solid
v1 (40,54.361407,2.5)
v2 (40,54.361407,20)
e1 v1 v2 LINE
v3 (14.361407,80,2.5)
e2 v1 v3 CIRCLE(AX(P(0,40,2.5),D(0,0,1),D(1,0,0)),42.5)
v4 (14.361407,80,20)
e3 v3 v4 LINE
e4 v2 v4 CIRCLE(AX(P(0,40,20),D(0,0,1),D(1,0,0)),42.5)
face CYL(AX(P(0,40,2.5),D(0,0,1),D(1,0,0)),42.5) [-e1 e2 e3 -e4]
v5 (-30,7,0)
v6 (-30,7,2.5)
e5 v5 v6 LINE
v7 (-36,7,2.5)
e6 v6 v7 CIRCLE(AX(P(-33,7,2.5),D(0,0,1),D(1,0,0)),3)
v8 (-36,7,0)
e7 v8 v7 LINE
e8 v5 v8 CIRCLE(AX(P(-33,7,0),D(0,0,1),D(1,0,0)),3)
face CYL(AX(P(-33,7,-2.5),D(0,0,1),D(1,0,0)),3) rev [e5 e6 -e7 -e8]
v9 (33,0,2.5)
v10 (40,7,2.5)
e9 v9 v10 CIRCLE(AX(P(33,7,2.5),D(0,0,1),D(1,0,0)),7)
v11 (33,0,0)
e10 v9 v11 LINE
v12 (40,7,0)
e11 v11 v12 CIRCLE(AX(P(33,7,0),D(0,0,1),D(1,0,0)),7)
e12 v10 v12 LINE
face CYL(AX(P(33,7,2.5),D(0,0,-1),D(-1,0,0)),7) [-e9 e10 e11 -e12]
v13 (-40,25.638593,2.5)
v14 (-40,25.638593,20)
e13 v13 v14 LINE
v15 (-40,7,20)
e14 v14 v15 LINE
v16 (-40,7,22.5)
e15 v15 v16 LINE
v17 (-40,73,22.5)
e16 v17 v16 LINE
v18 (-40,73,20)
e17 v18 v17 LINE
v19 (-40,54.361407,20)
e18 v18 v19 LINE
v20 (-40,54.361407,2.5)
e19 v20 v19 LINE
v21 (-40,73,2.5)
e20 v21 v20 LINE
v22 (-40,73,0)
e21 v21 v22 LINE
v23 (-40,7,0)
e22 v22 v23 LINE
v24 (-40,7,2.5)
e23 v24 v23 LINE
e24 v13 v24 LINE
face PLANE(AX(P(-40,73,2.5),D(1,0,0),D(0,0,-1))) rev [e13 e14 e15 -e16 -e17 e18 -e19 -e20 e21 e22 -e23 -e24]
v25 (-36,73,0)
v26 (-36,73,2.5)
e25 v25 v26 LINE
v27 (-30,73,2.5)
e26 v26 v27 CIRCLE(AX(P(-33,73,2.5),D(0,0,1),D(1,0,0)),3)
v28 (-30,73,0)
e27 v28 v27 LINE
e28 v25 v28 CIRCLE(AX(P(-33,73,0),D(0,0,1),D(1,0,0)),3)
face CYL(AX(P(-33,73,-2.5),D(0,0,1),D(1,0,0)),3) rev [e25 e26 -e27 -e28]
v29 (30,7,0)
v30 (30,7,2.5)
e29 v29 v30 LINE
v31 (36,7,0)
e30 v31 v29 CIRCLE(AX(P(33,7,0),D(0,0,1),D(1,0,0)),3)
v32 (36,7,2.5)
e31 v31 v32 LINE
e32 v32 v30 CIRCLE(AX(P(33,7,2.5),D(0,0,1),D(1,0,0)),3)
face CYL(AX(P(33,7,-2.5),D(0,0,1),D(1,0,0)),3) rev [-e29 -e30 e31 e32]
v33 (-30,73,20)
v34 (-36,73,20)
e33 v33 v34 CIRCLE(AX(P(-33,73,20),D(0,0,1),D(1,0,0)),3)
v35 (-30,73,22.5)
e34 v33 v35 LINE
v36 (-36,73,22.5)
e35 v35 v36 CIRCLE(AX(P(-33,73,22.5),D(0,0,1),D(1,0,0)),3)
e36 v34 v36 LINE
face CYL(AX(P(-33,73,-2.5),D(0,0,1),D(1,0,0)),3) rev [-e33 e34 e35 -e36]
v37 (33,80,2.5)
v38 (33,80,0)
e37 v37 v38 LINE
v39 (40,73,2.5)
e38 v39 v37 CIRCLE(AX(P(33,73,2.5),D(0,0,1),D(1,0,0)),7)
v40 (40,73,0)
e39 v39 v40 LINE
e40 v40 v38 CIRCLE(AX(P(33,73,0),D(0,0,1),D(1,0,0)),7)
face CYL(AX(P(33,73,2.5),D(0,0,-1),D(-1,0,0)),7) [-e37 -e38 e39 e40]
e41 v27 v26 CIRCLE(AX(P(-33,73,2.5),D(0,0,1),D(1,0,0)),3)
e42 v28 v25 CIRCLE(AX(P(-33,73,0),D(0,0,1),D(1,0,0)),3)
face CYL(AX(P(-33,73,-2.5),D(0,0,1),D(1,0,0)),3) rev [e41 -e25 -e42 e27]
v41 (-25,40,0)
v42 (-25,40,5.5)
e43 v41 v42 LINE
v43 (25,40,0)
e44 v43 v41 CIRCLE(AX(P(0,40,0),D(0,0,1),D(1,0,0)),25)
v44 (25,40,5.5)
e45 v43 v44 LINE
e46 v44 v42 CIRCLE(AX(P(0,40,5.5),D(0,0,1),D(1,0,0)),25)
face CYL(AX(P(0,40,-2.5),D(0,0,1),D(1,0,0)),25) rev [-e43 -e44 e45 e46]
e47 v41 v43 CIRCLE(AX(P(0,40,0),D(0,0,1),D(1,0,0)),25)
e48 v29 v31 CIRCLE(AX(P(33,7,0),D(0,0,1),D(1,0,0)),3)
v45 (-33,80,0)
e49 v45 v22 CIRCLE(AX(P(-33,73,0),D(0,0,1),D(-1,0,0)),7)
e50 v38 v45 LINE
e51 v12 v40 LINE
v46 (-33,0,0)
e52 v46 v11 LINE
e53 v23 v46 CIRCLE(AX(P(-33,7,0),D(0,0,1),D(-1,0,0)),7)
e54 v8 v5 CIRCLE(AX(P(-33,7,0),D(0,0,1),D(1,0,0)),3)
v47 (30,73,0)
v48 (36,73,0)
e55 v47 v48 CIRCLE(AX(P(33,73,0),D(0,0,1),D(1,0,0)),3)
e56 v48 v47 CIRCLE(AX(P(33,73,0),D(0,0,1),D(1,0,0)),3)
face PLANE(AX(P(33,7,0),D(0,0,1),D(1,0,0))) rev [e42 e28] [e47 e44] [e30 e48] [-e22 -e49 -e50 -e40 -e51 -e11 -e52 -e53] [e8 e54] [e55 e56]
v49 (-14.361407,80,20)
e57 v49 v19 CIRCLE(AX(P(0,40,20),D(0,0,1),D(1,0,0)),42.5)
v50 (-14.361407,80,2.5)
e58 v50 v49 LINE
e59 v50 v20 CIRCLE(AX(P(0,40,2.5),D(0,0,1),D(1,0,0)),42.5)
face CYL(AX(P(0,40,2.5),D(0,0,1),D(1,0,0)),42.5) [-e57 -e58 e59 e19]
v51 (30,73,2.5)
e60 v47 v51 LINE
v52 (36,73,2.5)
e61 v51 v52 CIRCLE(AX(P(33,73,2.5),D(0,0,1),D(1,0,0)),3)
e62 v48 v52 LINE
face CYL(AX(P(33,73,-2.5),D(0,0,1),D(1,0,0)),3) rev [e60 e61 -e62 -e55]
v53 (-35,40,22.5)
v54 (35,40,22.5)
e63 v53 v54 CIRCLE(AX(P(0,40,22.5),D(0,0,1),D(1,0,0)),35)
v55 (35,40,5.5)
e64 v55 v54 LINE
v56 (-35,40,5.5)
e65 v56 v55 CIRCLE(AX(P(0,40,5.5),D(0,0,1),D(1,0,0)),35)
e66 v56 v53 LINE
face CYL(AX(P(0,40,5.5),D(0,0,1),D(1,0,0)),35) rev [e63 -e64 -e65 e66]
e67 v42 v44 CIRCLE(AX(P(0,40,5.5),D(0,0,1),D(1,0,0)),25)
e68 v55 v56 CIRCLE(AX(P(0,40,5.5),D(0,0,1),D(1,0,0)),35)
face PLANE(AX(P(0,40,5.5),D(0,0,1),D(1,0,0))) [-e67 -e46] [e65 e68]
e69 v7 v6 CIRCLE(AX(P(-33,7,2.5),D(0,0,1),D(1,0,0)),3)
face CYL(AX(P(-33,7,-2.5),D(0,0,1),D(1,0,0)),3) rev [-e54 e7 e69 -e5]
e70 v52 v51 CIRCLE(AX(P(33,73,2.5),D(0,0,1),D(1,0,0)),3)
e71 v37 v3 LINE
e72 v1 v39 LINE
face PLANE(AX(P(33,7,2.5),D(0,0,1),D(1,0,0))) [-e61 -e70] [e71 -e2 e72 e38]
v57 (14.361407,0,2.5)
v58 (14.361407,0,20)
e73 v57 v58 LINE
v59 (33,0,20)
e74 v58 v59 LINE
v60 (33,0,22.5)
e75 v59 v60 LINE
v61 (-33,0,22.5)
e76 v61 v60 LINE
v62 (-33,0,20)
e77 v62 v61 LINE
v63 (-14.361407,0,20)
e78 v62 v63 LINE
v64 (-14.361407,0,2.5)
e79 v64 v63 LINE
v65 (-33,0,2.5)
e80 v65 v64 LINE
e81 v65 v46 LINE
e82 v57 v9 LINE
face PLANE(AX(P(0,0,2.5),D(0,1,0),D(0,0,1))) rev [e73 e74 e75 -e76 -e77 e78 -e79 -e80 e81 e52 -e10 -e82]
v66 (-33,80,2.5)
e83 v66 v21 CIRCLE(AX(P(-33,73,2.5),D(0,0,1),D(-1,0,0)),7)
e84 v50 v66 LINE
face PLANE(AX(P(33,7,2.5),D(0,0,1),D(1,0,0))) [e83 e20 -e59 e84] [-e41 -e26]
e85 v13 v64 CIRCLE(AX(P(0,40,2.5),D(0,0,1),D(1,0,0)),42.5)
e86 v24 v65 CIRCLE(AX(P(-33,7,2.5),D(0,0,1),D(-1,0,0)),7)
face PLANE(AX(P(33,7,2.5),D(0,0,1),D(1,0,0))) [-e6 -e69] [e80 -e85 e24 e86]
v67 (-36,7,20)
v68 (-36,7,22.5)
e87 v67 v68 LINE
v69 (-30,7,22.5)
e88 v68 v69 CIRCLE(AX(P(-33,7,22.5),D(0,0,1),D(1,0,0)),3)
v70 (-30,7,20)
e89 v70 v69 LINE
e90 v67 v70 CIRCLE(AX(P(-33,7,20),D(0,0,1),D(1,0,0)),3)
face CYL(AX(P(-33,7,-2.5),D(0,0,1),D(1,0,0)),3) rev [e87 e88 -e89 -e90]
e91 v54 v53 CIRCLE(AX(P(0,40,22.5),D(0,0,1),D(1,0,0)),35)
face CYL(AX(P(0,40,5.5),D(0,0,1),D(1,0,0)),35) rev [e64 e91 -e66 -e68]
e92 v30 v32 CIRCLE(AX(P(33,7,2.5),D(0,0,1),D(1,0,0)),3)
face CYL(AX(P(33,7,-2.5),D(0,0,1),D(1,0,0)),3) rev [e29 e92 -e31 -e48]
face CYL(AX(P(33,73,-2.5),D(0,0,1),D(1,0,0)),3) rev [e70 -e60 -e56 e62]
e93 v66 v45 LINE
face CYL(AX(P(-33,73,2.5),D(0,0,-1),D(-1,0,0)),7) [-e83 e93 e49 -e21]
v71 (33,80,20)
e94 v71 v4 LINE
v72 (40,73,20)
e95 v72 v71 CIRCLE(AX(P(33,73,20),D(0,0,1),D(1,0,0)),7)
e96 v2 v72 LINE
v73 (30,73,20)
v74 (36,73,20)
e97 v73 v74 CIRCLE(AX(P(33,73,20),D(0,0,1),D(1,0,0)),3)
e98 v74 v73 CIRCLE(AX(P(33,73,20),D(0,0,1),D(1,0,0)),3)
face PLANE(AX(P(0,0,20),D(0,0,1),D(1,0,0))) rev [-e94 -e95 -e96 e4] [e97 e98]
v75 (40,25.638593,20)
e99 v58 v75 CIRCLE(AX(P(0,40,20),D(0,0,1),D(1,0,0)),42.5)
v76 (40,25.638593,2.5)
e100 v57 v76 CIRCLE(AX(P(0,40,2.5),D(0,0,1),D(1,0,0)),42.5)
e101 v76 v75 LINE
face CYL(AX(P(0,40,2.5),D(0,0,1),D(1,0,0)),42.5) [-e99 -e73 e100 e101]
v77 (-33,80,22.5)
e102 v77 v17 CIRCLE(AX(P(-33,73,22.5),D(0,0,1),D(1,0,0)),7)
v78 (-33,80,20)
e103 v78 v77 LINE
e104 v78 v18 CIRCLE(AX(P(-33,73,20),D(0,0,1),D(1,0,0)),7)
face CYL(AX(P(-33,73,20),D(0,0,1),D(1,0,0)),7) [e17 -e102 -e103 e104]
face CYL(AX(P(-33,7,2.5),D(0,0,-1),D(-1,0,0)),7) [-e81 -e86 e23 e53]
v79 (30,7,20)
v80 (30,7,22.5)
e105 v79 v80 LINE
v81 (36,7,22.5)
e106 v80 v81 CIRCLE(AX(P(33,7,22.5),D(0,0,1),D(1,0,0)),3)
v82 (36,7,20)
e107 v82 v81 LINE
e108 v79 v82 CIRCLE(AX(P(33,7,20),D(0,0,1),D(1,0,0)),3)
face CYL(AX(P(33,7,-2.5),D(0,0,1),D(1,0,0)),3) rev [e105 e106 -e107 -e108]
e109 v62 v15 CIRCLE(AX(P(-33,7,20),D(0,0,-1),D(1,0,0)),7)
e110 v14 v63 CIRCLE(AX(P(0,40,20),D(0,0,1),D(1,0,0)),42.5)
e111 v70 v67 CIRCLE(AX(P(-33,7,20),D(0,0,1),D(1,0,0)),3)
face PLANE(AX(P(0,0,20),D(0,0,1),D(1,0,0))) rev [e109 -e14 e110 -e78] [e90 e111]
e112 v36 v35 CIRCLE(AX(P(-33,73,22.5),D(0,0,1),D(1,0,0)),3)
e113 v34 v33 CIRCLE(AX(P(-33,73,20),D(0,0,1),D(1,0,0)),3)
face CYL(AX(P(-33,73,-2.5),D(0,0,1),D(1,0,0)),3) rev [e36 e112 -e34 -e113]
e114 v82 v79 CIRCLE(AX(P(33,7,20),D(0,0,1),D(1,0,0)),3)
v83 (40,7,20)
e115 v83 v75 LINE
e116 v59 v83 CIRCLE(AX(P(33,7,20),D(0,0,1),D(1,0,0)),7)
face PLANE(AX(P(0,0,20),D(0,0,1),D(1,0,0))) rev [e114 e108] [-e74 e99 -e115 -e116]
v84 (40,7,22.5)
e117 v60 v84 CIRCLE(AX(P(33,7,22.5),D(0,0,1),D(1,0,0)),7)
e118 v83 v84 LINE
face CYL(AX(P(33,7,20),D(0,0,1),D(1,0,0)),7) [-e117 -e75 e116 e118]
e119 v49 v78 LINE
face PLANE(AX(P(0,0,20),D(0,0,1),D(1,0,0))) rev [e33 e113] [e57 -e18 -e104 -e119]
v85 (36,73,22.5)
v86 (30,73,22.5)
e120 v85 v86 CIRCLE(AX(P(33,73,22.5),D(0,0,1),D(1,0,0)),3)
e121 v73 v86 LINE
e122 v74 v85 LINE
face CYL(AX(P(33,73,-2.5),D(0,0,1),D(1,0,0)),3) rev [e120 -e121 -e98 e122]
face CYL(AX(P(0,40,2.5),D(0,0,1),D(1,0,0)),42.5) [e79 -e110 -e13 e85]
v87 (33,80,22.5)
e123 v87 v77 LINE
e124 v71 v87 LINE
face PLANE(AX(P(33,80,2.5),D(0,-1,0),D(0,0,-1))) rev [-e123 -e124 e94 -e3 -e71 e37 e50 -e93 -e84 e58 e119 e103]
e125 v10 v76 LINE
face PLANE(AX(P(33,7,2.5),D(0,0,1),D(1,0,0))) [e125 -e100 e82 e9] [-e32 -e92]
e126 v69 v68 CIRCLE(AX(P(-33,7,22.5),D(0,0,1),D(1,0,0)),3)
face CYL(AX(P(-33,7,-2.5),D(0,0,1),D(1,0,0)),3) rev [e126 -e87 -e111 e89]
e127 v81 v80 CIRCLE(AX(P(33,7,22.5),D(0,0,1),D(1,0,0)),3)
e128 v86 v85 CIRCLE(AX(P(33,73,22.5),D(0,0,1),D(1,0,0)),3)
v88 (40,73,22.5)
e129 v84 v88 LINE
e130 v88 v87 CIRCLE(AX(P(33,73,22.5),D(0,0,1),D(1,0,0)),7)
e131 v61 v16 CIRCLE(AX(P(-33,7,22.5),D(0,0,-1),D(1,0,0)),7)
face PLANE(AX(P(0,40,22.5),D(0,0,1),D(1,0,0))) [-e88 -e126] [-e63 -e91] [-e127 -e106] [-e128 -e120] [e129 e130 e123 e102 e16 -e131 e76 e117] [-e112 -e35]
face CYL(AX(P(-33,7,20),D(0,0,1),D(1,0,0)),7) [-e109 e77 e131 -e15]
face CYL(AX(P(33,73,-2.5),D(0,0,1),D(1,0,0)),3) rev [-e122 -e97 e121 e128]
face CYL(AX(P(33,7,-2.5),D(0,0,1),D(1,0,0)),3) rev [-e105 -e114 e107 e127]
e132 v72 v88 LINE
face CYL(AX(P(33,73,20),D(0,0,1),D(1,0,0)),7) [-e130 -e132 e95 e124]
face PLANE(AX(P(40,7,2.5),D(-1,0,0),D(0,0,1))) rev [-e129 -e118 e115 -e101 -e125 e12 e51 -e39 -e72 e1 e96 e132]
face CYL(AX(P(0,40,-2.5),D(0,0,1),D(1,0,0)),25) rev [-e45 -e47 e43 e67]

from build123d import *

# Parameters (mm, degrees)
FRONT_FLANGE_80X80_DEPTH = 2.5
HUB_SKETCH_R             = 35
HUB_70_DEPTH             = 20
REAR_START               = -2.5
REAR_FLANGE_80X80_DEPTH  = 2.5
SIDE_WEBS_DEPTH          = 20
LARGE_BORE_SKETCH_R      = 35
LARGE_BORE_70_DEPTH      = 17
THROUGH_BORE_SKETCH_R    = 25
THROUGH_BORE_50_DEPTH    = 8
CORNER_HOLES_SKETCH_R    = 3
CORNER_HOLES_4X_6_DEPTH  = 25


with BuildPart() as part:
    # Front Flange Sketch → Front Flange 80x80 (new body)
    with BuildSketch(Plane.XY):
        with BuildLine():
            Line((0, 0), (33, 0))
            ThreePointArc((33, 0), (37.949747468, 2.050252532), (40, 7))
            Line((40, 7), (40, 73))
            ThreePointArc((40, 73), (37.949747468, 77.949747468), (33, 80))
            Line((33, 80), (-33, 80))
            ThreePointArc((-33, 80), (-37.949747468, 77.949747468), (-40, 73))
            Line((-40, 73), (-40, 7))
            ThreePointArc((-40, 7), (-37.949747468, 2.050252532), (-33, 0))
            Line((-33, 0), (0, 0))
        make_face()
    extrude(amount=FRONT_FLANGE_80X80_DEPTH)

    # Hub Sketch → Hub Ø70 (add)
    with BuildSketch(Plane.XY.offset(2.5)):
        with Locations((0, 40)):
            Circle(HUB_SKETCH_R)
    extrude(amount=HUB_70_DEPTH)

    # Rear Flange Sketch → Rear Flange 80x80 (add)
    with BuildSketch(Plane.XY.offset(22.5).offset(REAR_START)):
        with BuildLine():
            Line((40, 7), (40, 40))
            Line((40, 40), (40, 73))
            ThreePointArc((40, 73), (37.949747468, 77.949747468), (33, 80))
            Line((33, 80), (-33, 80))
            ThreePointArc((-33, 80), (-37.949747468, 77.949747468), (-40, 73))
            Line((-40, 73), (-40, 7))
            ThreePointArc((-40, 7), (-37.949747468, 2.050252532), (-33, 0))
            Line((-33, 0), (33, 0))
            ThreePointArc((33, 0), (37.949747468, 2.050252532), (40, 7))
        make_face()
    extrude(amount=REAR_FLANGE_80X80_DEPTH)

    # Side Web Sketch → Side Webs (add)
    with BuildSketch(Plane.XY.offset(22.5)):
        with BuildLine():
            Line((-14.361406616, 80), (14.361406616, 80))
            ThreePointArc((14.361406616, 80), (30.0520382, 70.0520382), (40, 54.361406616))
            Line((40, 54.361406616), (40, 25.638593384))
            ThreePointArc((40, 25.638593384), (30.0520382, 9.9479618), (14.361406616, 0))
            Line((14.361406616, 0), (-14.361406616, 0))
            ThreePointArc((-14.361406616, 0), (-30.0520382, 9.9479618), (-40, 25.638593384))
            Line((-40, 25.638593384), (-40, 54.361406616))
            ThreePointArc((-40, 54.361406616), (-30.0520382, 70.0520382), (-14.361406616, 80))
        make_face()
    extrude(amount=-SIDE_WEBS_DEPTH)

    # Large Bore Sketch → Large Bore Ø70 (cut)
    with BuildSketch(Plane.XY.offset(22.5)):
        with Locations((0, 40)):
            Circle(LARGE_BORE_SKETCH_R)
    extrude(amount=-LARGE_BORE_70_DEPTH, mode=Mode.SUBTRACT)

    # Through Bore Sketch → Through Bore Ø50 (cut)
    with BuildSketch(Plane.XY.offset(5.5)):
        with Locations((0, 40)):
            Circle(THROUGH_BORE_SKETCH_R)
    extrude(amount=-THROUGH_BORE_50_DEPTH, mode=Mode.SUBTRACT)

    # Corner Holes Sketch → Corner Holes 4xØ6 (cut)
    with BuildSketch(Plane.XY.offset(22.5)):
        with Locations((-33, 73)):
            Circle(CORNER_HOLES_SKETCH_R)
        with Locations((33, 73)):
            Circle(CORNER_HOLES_SKETCH_R)
        with Locations((-33, 7)):
            Circle(CORNER_HOLES_SKETCH_R)
        with Locations((33, 7)):
            Circle(CORNER_HOLES_SKETCH_R)
    extrude(amount=-CORNER_HOLES_4X_6_DEPTH, mode=Mode.SUBTRACT)


solid = part.part
